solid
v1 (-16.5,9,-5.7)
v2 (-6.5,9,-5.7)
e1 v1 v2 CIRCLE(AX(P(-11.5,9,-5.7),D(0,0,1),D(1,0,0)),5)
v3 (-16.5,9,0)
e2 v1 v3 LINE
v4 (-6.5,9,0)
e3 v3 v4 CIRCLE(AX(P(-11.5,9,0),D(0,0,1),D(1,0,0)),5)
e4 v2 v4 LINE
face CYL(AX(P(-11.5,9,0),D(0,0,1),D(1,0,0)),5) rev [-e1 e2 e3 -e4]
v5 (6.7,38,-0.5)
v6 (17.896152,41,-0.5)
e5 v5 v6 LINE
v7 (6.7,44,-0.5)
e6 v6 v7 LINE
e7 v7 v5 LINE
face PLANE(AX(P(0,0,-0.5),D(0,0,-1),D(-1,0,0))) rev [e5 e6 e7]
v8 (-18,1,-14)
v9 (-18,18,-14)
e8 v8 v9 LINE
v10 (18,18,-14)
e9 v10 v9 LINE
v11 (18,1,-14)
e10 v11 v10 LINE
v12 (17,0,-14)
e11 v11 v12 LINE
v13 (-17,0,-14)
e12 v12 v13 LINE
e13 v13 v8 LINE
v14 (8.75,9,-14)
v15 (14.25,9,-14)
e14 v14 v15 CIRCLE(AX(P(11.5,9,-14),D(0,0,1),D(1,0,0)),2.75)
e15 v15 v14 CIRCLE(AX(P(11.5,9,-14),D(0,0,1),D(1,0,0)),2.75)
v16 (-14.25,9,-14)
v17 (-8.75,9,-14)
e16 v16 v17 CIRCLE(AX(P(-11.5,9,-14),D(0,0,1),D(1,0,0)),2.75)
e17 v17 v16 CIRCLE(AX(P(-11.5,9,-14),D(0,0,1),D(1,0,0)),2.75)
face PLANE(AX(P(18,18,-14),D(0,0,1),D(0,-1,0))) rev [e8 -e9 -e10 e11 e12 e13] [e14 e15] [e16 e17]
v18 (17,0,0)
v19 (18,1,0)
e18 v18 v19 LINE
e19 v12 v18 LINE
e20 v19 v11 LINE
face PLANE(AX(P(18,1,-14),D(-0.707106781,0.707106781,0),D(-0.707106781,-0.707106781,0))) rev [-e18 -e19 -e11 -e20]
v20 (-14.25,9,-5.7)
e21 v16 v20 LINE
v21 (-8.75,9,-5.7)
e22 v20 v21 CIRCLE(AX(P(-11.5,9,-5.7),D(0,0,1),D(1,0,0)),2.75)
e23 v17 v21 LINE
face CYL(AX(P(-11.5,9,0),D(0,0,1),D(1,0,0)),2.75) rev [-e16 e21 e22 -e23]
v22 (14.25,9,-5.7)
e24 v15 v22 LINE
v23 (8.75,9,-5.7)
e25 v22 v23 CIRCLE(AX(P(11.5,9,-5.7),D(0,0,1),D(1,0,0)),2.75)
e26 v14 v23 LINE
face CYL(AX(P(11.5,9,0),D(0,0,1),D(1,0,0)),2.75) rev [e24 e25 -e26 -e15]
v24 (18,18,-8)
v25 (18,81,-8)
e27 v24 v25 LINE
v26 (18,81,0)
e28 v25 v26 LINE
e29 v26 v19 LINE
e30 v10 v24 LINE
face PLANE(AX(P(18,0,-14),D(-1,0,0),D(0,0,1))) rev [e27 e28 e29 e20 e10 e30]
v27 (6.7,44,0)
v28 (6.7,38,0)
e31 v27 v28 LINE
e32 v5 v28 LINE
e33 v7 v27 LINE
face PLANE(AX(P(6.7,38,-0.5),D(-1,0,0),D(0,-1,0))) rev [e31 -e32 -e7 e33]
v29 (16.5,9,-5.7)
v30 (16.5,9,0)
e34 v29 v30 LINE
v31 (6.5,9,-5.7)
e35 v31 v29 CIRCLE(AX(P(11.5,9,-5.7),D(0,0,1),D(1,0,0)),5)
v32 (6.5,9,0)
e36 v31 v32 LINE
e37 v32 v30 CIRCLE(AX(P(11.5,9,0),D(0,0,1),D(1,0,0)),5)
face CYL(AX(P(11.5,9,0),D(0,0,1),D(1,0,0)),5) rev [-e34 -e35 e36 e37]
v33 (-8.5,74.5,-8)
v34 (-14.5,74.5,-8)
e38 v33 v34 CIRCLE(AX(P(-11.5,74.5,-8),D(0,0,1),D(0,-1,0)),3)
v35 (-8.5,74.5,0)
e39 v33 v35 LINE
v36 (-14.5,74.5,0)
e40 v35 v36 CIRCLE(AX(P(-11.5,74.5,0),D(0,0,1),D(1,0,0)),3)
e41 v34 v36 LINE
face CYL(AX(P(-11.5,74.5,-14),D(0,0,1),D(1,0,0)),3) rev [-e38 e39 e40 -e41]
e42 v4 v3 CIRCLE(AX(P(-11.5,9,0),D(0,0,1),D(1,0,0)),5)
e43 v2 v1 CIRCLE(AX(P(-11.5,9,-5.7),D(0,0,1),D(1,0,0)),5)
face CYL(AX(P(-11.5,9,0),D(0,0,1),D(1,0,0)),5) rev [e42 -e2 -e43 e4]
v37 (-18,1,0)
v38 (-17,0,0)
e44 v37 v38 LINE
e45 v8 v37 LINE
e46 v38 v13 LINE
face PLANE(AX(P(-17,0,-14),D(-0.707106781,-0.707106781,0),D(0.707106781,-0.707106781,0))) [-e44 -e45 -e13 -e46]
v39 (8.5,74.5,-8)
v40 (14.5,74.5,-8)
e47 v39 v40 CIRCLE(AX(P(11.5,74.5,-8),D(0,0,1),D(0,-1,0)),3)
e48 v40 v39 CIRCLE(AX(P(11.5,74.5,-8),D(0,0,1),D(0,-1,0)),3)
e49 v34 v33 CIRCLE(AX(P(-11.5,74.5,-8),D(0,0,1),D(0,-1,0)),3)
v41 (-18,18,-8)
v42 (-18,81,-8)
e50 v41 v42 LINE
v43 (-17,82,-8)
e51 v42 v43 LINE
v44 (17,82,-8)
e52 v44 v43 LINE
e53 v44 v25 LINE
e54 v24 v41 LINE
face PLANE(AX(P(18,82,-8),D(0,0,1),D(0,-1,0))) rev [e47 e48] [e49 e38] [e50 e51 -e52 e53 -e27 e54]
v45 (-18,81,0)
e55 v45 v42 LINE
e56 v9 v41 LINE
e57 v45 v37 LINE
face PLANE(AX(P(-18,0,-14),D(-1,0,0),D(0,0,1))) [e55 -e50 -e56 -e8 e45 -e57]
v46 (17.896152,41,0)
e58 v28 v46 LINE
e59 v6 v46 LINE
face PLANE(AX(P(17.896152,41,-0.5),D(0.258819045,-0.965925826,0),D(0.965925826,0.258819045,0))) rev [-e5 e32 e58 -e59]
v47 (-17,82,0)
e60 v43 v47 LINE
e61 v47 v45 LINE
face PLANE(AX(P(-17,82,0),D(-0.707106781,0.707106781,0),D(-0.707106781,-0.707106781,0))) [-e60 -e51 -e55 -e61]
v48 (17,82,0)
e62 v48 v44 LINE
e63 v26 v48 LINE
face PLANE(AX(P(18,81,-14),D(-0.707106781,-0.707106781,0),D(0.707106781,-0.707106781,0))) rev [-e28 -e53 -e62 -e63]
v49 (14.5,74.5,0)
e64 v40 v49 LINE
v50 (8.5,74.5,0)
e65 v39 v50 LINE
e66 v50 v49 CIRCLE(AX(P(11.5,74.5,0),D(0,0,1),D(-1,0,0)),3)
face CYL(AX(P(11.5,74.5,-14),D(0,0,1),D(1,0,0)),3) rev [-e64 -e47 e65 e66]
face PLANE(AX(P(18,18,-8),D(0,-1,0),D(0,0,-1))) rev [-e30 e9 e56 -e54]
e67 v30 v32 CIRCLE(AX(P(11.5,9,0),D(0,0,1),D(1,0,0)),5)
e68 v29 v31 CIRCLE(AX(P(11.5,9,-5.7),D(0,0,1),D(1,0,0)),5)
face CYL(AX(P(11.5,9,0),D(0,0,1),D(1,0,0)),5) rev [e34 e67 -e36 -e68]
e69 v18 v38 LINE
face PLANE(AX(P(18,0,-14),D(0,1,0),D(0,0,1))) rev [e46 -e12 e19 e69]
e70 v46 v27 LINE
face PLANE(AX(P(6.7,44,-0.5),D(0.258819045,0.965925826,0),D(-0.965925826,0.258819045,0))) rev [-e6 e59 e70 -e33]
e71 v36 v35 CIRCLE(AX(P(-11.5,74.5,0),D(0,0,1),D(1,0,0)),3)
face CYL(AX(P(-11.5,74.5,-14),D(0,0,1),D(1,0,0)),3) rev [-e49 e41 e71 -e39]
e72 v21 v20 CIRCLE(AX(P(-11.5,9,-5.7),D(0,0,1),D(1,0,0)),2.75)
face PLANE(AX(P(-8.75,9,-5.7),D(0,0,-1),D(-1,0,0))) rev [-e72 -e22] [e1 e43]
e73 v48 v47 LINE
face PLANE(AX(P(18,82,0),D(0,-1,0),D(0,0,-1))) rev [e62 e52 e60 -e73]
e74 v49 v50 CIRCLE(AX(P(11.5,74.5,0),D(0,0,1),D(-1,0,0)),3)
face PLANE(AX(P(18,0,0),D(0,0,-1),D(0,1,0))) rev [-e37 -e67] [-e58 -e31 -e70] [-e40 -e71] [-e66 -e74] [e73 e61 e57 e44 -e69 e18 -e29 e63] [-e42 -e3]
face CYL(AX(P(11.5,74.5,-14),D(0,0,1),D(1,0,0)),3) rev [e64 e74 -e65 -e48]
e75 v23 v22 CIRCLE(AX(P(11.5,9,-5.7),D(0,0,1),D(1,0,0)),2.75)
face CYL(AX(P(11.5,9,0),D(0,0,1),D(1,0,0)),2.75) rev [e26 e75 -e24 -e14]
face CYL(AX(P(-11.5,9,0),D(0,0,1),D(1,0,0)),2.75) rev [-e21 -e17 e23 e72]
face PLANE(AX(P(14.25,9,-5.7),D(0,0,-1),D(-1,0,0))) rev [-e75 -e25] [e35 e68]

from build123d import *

# Parameters (mm, degrees)
BOSS_EXTRUDE1_DEPTH                                  = 18
HOLE_SIZE_PER_SOCKET_HEAD_CAP_SCREW_TYPE_D           = 5.5
HOLE_SIZE_PER_SOCKET_HEAD_CAP_SCREW_TYPE_CBORE_D     = 10
HOLE_SIZE_PER_SOCKET_HEAD_CAP_SCREW_TYPE_CBORE_DEPTH = 5.7
SKETCH5_R                                            = 3
CUT_EXTRUDE1_DEPTH                                   = 86.111691324
CHAMFER1_SIZE                                        = 1
CUT_EXTRUDE3_DEPTH                                   = 0.5


with BuildPart() as part:
    # Sketch1 → Boss-Extrude1 (new, symmetric)
    with BuildSketch(Plane(origin=(0, 0, 0), x_dir=(0, 0, -1), z_dir=(1, 0, 0))):
        Polygon((14, 0), (0, 0), (0, 82), (8, 82), (8, 18), (14, 18), align=None)
    extrude(amount=BOSS_EXTRUDE1_DEPTH, both=True)

    # Hole size per socket head cap screw type1 (through all)
    with Locations(Plane.XY):
        with Locations((11.5, 9), (-11.5, 9)):
            CounterBoreHole(HOLE_SIZE_PER_SOCKET_HEAD_CAP_SCREW_TYPE_D / 2, HOLE_SIZE_PER_SOCKET_HEAD_CAP_SCREW_TYPE_CBORE_D / 2, HOLE_SIZE_PER_SOCKET_HEAD_CAP_SCREW_TYPE_CBORE_DEPTH)

    # Sketch5 → Cut-Extrude1 (cut, through all)
    with BuildSketch(Plane.XY):
        with Locations((-11.5, 74.5)):
            Circle(SKETCH5_R)
        with Locations(Location((11.5, 74.5, 0), (0, 0, 270))):
            Circle(SKETCH5_R)
    extrude(amount=-CUT_EXTRUDE1_DEPTH, mode=Mode.SUBTRACT)

    # Chamfer1
    chamfer1_edges = [part.edges().sort_by_distance(p)[0] for p in [
        (18, 82, -4),
        (18, 0, -7),
        (-18, 0, -7),
        (-18, 82, -4),
    ]]
    chamfer(chamfer1_edges, length=CHAMFER1_SIZE)

    # Sketch6 → Cut-Extrude3 (cut)
    with BuildSketch(Plane.XY):
        Polygon((6.7, 44), (17.896152423, 41), (6.7, 38), align=None)
    extrude(amount=-CUT_EXTRUDE3_DEPTH, mode=Mode.SUBTRACT)


solid = part.part
